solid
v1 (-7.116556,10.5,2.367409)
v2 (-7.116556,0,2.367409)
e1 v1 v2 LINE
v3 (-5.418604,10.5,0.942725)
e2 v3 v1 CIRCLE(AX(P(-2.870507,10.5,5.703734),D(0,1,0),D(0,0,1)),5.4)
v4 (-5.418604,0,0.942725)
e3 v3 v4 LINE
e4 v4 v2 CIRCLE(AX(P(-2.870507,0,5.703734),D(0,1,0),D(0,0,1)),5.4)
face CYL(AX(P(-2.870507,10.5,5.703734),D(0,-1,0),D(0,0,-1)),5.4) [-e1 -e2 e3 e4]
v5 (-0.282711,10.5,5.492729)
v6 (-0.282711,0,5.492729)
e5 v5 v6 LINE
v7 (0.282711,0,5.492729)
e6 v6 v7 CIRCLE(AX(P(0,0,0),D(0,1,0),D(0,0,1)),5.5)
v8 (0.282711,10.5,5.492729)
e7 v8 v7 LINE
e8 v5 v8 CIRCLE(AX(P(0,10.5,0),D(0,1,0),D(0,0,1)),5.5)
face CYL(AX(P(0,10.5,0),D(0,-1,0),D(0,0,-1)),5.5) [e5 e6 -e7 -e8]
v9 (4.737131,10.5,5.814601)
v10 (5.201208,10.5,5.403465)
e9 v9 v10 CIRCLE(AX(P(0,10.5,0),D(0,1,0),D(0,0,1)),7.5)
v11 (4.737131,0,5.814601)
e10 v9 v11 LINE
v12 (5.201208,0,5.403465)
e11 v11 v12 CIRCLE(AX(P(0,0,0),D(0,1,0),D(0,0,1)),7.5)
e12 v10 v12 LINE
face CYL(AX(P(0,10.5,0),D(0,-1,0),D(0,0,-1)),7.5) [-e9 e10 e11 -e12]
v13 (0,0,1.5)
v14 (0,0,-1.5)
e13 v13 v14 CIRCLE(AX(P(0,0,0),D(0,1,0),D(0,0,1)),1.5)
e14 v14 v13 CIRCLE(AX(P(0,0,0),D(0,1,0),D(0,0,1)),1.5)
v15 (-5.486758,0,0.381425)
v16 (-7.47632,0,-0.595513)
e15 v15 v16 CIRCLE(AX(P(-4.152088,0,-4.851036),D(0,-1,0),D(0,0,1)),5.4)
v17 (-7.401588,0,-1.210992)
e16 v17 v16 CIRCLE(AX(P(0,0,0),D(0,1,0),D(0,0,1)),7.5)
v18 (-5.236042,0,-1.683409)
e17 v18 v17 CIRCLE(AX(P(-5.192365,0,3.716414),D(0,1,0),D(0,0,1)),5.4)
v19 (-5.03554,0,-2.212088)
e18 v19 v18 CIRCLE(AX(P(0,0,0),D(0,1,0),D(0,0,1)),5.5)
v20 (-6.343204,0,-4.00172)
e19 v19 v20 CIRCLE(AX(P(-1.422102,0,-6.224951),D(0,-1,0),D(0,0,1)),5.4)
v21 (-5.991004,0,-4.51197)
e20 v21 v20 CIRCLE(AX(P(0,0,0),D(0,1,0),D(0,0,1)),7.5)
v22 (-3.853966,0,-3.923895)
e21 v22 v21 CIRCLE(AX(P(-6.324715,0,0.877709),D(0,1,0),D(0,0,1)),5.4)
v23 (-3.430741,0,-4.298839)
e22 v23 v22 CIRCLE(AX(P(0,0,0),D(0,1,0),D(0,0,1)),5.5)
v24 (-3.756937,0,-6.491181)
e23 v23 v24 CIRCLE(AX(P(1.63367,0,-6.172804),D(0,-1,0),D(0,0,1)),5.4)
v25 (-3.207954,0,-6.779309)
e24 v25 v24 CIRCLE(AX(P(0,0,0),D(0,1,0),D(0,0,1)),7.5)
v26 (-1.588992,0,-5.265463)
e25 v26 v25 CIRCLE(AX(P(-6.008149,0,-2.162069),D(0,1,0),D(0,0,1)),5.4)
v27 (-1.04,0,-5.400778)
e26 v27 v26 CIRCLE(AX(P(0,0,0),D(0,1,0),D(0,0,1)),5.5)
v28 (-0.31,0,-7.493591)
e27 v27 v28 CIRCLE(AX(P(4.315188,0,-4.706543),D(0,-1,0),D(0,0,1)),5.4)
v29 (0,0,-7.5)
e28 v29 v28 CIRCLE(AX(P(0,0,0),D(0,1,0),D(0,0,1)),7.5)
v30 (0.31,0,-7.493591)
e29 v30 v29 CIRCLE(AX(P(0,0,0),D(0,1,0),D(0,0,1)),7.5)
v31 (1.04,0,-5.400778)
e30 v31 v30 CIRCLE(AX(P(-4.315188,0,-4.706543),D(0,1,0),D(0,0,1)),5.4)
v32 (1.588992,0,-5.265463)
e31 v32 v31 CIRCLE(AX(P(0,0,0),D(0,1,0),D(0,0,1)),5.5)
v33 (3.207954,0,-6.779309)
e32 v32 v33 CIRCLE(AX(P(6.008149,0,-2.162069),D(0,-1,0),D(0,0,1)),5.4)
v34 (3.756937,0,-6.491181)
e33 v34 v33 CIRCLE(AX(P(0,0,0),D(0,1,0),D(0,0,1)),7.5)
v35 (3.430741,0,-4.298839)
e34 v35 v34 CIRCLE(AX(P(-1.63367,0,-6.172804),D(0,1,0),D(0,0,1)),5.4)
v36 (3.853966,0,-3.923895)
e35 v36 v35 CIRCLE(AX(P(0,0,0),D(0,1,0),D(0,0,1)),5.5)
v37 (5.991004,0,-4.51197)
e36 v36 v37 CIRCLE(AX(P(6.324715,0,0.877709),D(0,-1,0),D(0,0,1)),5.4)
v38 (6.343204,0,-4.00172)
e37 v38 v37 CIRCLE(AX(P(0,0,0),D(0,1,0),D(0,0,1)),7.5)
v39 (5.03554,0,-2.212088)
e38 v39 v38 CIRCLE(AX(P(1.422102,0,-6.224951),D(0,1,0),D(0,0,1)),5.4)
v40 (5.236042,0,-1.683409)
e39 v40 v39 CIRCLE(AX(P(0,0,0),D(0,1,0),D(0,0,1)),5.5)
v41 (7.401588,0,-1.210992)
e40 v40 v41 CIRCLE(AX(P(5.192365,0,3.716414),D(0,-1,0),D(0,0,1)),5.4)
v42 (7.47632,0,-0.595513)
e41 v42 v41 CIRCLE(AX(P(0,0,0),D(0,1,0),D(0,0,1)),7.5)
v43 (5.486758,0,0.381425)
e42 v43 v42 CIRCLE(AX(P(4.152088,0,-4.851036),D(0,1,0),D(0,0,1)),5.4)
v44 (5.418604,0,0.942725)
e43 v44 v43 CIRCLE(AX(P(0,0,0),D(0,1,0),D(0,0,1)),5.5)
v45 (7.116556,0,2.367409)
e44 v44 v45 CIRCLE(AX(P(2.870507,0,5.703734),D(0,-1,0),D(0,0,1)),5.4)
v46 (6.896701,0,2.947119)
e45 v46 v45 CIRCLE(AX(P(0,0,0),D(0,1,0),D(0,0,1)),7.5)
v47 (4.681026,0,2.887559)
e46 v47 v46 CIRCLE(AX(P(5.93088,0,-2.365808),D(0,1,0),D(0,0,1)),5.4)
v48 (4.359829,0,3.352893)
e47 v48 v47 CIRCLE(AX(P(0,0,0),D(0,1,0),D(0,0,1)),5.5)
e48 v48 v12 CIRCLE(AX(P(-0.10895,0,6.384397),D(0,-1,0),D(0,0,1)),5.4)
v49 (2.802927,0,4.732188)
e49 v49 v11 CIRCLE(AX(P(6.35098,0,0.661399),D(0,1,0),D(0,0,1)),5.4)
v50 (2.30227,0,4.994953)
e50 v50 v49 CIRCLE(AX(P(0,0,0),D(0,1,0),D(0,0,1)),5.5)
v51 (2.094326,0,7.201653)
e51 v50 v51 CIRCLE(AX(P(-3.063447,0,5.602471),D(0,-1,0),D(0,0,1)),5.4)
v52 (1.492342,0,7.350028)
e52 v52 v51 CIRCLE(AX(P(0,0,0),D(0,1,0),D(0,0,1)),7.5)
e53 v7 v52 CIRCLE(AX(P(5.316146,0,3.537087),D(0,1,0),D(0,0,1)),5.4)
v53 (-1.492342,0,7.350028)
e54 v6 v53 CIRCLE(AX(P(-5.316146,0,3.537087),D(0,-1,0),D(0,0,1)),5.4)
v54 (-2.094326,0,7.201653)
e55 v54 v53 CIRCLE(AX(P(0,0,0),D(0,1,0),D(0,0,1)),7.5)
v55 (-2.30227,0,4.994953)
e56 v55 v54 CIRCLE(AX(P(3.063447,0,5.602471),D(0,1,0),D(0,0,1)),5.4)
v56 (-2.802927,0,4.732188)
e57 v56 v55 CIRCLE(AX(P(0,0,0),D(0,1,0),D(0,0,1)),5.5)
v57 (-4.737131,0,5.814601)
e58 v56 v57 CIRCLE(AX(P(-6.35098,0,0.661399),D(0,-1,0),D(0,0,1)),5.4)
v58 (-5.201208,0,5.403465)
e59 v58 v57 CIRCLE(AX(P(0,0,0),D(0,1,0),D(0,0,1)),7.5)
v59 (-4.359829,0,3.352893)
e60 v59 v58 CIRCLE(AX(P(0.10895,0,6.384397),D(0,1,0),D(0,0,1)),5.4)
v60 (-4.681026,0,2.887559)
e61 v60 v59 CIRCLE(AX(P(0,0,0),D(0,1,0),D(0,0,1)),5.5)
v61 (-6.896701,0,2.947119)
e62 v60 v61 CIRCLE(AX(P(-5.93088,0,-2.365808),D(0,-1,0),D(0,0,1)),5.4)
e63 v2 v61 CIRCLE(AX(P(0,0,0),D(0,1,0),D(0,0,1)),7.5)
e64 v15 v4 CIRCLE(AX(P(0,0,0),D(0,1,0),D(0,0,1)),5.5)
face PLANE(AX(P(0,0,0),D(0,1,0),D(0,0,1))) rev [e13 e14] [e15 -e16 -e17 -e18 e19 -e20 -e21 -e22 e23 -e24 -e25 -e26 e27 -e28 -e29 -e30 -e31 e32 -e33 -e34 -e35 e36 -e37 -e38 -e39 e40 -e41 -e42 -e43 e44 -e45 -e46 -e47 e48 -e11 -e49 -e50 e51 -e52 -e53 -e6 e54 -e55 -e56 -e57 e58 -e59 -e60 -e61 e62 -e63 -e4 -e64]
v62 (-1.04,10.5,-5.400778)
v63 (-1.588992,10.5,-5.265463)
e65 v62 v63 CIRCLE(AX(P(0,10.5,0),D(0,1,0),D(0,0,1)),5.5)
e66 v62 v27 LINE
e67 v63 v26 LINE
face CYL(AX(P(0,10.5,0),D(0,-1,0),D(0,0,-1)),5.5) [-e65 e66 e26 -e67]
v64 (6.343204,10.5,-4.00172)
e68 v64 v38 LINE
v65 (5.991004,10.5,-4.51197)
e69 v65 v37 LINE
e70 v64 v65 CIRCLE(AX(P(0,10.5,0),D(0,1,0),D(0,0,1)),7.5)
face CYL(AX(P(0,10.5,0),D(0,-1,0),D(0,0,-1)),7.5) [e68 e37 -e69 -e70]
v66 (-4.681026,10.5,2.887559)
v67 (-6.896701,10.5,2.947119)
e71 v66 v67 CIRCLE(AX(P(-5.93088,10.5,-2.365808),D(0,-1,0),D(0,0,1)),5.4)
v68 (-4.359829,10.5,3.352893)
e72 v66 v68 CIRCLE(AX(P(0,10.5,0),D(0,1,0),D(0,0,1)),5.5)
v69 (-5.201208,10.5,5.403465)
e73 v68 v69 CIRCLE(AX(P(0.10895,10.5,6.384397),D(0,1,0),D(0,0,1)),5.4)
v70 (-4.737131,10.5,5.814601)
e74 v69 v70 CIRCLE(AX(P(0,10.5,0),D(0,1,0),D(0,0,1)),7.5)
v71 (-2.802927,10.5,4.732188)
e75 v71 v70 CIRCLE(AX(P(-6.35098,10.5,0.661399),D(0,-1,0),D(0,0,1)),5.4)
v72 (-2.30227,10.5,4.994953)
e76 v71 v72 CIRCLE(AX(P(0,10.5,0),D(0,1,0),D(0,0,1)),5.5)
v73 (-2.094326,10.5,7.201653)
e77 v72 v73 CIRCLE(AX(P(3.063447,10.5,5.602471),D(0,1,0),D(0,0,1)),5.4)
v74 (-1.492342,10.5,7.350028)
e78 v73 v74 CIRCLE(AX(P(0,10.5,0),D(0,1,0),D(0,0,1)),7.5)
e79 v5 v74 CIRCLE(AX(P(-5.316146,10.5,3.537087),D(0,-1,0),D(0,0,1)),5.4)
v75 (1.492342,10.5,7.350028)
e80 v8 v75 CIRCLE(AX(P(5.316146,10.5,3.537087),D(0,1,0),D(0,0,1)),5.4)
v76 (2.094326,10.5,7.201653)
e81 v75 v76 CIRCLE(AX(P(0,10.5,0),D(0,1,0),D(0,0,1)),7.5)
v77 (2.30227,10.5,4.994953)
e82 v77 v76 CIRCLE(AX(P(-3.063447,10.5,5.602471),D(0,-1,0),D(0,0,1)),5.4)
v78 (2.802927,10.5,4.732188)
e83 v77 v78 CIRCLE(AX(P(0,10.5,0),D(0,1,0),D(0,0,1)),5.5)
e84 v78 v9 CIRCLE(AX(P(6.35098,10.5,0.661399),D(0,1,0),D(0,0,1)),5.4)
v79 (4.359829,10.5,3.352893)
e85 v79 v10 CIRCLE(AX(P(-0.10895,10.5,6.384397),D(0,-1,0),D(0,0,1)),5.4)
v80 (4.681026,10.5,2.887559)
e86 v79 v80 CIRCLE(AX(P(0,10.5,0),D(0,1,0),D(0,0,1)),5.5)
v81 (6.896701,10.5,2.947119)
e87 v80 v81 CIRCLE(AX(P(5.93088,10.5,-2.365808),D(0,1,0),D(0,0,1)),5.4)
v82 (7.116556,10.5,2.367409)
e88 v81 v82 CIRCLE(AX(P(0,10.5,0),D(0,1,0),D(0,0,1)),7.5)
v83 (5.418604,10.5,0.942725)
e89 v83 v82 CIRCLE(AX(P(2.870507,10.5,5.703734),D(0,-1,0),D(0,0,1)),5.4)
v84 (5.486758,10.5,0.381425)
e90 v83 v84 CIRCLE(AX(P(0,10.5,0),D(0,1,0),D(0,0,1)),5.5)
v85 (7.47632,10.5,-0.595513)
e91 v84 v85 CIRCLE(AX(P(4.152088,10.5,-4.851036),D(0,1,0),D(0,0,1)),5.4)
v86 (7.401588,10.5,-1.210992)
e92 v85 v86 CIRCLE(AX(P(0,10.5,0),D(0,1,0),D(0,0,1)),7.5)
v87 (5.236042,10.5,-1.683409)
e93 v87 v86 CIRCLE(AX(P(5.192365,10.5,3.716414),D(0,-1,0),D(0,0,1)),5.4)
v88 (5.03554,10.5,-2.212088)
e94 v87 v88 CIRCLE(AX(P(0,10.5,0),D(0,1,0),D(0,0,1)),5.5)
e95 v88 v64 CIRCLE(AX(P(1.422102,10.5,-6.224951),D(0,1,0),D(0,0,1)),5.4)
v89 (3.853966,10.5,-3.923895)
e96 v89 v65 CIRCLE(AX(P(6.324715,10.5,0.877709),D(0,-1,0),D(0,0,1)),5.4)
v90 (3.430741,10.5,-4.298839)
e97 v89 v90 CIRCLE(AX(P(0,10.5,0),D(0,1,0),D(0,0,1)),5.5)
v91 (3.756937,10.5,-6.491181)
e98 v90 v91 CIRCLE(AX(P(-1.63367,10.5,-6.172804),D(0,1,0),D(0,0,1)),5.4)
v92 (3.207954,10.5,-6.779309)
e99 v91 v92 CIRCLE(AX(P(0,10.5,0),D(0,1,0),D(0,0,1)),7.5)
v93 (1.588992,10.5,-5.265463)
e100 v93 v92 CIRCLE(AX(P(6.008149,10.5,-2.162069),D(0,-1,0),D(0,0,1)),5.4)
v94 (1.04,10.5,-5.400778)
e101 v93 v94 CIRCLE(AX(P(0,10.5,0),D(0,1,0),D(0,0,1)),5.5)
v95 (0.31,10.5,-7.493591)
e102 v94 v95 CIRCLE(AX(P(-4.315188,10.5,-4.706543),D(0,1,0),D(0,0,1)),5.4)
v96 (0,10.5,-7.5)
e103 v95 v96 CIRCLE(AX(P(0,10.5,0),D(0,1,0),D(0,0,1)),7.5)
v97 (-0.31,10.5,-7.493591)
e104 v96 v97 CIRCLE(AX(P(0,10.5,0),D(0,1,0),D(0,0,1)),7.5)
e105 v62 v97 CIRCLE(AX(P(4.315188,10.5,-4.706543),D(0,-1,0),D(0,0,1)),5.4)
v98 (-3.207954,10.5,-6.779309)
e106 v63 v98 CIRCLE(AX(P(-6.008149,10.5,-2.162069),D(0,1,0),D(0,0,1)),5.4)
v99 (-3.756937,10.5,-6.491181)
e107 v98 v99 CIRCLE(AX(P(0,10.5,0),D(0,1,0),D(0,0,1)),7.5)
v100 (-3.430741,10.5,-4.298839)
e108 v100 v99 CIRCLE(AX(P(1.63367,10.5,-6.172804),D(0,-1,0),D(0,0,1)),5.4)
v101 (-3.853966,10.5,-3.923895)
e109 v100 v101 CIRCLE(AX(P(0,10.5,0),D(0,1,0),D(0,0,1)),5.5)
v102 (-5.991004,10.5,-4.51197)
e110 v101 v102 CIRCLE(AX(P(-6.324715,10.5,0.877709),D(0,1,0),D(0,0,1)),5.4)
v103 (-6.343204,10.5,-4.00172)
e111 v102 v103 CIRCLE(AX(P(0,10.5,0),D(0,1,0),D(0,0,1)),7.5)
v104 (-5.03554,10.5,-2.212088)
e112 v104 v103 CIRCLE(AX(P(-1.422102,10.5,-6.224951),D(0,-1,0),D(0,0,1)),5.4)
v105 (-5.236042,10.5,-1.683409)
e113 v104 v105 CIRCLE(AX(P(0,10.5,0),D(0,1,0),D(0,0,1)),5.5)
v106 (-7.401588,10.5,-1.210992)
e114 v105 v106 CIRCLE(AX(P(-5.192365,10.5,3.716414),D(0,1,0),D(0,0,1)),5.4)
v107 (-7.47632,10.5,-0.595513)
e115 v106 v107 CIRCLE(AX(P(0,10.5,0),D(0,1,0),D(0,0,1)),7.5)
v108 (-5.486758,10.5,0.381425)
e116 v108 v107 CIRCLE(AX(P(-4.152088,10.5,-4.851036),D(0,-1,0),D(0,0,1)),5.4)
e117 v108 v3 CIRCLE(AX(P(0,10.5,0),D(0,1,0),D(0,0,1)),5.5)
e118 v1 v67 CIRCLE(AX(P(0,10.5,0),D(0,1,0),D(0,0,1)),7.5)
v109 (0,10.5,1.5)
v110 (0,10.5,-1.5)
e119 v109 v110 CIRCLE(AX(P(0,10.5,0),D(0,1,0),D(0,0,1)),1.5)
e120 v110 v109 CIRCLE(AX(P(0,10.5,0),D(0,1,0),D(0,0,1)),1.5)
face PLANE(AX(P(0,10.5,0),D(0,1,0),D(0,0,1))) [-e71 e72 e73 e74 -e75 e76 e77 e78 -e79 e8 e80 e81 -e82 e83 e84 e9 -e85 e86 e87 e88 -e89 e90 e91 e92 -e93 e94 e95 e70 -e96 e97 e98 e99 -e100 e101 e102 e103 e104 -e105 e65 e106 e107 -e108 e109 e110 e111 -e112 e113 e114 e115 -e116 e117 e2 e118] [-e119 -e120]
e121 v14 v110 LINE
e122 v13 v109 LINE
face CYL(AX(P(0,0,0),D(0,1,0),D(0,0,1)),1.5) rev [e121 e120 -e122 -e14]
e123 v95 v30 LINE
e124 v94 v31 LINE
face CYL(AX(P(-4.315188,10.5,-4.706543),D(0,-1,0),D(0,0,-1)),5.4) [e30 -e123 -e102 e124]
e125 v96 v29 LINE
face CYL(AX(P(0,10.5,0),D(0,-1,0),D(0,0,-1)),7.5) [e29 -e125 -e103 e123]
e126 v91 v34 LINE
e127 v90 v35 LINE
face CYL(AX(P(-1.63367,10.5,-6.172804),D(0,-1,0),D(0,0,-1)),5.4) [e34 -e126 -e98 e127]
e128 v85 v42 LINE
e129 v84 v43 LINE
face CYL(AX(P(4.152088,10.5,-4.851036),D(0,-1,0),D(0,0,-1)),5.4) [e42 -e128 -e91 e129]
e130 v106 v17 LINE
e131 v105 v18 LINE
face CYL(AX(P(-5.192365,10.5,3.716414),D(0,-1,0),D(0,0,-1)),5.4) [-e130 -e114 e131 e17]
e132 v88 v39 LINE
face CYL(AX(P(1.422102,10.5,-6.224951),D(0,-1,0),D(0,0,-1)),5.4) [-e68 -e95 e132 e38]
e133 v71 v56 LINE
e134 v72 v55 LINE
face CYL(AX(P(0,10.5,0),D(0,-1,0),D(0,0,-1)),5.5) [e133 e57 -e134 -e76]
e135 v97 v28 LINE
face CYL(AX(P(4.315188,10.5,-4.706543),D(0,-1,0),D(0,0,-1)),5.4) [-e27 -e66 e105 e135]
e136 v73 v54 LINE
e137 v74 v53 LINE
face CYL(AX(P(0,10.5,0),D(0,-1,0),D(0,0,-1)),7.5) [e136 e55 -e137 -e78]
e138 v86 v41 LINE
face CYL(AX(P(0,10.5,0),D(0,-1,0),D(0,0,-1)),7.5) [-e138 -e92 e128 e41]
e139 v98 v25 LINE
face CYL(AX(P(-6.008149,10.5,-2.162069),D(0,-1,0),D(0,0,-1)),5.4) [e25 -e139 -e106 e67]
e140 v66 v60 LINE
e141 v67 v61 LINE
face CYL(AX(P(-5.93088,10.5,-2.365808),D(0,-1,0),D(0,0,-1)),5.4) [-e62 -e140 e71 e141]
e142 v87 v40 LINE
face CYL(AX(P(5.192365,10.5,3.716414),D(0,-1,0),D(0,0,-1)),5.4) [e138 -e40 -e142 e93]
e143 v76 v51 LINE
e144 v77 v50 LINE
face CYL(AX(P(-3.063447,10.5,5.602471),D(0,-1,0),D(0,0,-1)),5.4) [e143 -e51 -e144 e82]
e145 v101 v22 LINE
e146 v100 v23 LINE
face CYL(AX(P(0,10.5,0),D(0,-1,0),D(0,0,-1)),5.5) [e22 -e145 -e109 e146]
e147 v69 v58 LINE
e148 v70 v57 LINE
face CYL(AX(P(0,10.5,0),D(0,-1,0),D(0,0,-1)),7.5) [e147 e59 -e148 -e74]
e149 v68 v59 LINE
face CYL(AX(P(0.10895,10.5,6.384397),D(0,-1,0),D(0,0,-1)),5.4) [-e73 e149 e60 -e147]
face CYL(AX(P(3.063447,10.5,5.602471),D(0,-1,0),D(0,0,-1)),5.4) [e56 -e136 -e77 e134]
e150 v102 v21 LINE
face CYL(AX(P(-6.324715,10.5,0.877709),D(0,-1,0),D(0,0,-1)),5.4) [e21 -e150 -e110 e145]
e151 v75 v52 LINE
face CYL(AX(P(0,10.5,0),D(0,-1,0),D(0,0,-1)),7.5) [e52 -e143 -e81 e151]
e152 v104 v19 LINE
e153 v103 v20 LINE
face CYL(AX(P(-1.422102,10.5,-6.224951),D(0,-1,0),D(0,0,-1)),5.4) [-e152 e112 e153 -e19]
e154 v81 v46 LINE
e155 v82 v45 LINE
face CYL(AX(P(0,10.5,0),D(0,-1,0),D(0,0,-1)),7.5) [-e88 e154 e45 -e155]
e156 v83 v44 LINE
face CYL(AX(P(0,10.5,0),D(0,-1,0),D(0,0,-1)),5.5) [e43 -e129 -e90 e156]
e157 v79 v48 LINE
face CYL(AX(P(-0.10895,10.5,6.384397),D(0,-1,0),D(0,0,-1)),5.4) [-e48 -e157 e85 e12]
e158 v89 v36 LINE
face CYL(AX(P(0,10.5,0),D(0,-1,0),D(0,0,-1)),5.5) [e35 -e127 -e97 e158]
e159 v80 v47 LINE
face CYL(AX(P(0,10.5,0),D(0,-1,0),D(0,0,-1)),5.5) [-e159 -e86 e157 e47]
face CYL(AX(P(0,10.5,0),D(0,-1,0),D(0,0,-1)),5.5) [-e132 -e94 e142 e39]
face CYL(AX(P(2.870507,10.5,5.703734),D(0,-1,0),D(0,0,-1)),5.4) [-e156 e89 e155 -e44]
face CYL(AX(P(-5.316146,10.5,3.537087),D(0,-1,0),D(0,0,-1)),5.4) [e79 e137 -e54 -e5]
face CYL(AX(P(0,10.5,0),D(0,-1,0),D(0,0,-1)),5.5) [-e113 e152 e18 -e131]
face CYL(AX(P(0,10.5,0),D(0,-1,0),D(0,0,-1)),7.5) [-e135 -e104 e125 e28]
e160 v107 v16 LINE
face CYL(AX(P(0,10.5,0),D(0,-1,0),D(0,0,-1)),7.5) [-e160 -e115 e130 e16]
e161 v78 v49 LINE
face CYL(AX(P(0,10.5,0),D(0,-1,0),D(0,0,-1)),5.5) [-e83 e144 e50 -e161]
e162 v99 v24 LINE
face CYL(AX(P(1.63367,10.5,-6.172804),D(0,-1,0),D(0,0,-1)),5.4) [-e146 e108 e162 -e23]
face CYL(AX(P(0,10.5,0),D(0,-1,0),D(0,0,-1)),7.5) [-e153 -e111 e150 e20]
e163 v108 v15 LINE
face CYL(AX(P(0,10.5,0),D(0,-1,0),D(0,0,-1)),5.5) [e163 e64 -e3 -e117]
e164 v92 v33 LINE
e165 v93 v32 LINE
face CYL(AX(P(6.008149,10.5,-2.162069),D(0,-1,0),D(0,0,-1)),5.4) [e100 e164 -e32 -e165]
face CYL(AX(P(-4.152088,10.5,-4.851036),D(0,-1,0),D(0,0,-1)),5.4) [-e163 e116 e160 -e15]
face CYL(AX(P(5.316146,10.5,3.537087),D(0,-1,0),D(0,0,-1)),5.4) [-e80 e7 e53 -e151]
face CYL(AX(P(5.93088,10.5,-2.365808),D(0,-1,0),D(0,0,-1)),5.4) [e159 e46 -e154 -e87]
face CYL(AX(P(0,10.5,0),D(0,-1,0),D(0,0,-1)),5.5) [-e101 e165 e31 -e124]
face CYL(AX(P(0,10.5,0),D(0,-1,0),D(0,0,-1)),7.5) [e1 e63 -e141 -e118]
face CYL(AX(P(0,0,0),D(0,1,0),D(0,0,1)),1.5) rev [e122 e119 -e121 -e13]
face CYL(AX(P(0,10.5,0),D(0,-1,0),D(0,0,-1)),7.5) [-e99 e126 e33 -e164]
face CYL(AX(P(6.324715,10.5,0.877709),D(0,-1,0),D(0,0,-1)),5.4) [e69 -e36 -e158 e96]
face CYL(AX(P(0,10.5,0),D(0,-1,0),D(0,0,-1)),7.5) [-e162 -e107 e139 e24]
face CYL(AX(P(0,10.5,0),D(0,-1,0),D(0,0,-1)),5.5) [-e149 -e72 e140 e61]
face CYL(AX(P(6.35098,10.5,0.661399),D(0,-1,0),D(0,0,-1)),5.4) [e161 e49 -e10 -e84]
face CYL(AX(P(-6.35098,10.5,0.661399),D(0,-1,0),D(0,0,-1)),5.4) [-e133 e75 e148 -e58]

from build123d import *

# Parameters (mm, degrees)
BOSS_EXTRUDE1_DEPTH = 10.5
SKETCH2_R           = 1.5
CUT_EXTRUDE1_DEPTH  = 10.5


with BuildPart() as part:
    # Sketch1 → Boss-Extrude1 (new body)
    with BuildSketch(Plane(origin=(0, 0, 0), x_dir=(1, 0, 0), z_dir=(0, 1, 0))):
        with BuildLine():
            ThreePointArc((1.04, 5.400777722), (0.783531714, 6.485041414), (0.31, 7.493590595))
            ThreePointArc((0.31, 7.493590595), (0, 7.5), (-0.31, 7.493590595))
            ThreePointArc((-0.31, 7.493590595), (-0.783531714, 6.485041414), (-1.04, 5.400777722))
            ThreePointArc((-1.04, 5.400777722), (-1.316236154, 5.340179996), (-1.588992288, 5.265463276))
            ThreePointArc((-1.588992288, 5.265463276), (-2.319966139, 6.10634434), (-3.207953823, 6.779309129))
            ThreePointArc((-3.207953823, 6.779309129), (-3.48542379, 6.640920192), (-3.756936559, 6.491180762))
            ThreePointArc((-3.756936559, 6.491180762), (-3.707531894, 5.378093653), (-3.430740821, 4.298839078))
            ThreePointArc((-3.430740821, 4.298839078), (-3.64717462, 4.116809115), (-3.853965592, 3.923894649))
            ThreePointArc((-3.853965592, 3.923894649), (-4.891987708, 4.328757368), (-5.991004086, 4.511969642))
            ThreePointArc((-5.991004086, 4.511969642), (-6.172378994, 4.2604856), (-6.343204228, 4.001719645))
            ThreePointArc((-6.343204228, 4.001719645), (-5.782181198, 3.039089449), (-5.035540265, 2.212088208))
            ThreePointArc((-5.035540265, 2.212088208), (-5.142589335, 1.950326879), (-5.236041824, 1.683409046))
            ThreePointArc((-5.236041824, 1.683409046), (-6.343313848, 1.559504249), (-7.401587511, 1.210992284))
            ThreePointArc((-7.401587511, 1.210992284), (-7.445316556, 0.904025102), (-7.476320253, 0.595512782))
            ThreePointArc((-7.476320253, 0.595512782), (-6.532202472, 0.003866477), (-5.486758119, -0.381425412))
            ThreePointArc((-5.486758119, -0.381425412), (-5.459898808, -0.662951741), (-5.418603976, -0.942725282))
            ThreePointArc((-5.418603976, -0.942725282), (-6.341463231, -1.567012498), (-7.116556437, -2.367408811))
            ThreePointArc((-7.116556437, -2.367408811), (-7.01262182, -2.659536653), (-6.896701407, -2.947118882))
            ThreePointArc((-6.896701407, -2.947118882), (-5.785774881, -3.032242258), (-4.68102581, -2.887559066))
            ThreePointArc((-4.68102581, -2.887559066), (-4.526411262, -3.124356107), (-4.359829258, -3.352892609))
            ThreePointArc((-4.359829258, -3.352892609), (-4.886859811, -4.334545567), (-5.201208047, -5.403465078))
            ThreePointArc((-5.201208047, -5.403465078), (-4.973419937, -5.613830611), (-4.737131383, -5.814601127))
            ThreePointArc((-4.737131383, -5.814601127), (-3.713895991, -5.373700834), (-2.802926901, -4.732187738))
            ThreePointArc((-2.802926901, -4.732187738), (-2.555977446, -4.870008141), (-2.302270198, -4.994952646))
            ThreePointArc((-2.302270198, -4.994952646), (-2.312735701, -6.109086484), (-2.094325574, -7.201652615))
            ThreePointArc((-2.094325574, -7.201652615), (-1.794867482, -7.282063631), (-1.492341648, -7.350028327))
            ThreePointArc((-1.492341648, -7.350028327), (-0.791208287, -6.484109309), (-0.282711218, -5.492729228))
            ThreePointArc((-0.282711218, -5.492729228), (0, -5.5), (0.282711218, -5.492729228))
            ThreePointArc((0.282711218, -5.492729228), (0.791208287, -6.484109309), (1.492341648, -7.350028327))
            ThreePointArc((1.492341648, -7.350028327), (1.794867482, -7.282063631), (2.094325574, -7.201652615))
            ThreePointArc((2.094325574, -7.201652615), (2.312735701, -6.109086484), (2.302270198, -4.994952646))
            ThreePointArc((2.302270198, -4.994952646), (2.555977446, -4.870008141), (2.802926901, -4.732187738))
            ThreePointArc((2.802926901, -4.732187738), (3.713895991, -5.373700834), (4.737131383, -5.814601127))
            ThreePointArc((4.737131383, -5.814601127), (4.973419937, -5.613830611), (5.201208047, -5.403465078))
            ThreePointArc((5.201208047, -5.403465078), (4.886859811, -4.334545567), (4.359829258, -3.352892609))
            ThreePointArc((4.359829258, -3.352892609), (4.526411262, -3.124356107), (4.68102581, -2.887559066))
            ThreePointArc((4.68102581, -2.887559066), (5.785774881, -3.032242258), (6.896701407, -2.947118882))
            ThreePointArc((6.896701407, -2.947118882), (7.01262182, -2.659536653), (7.116556437, -2.367408811))
            ThreePointArc((7.116556437, -2.367408811), (6.341463231, -1.567012498), (5.418603976, -0.942725282))
            ThreePointArc((5.418603976, -0.942725282), (5.459898808, -0.662951741), (5.486758119, -0.381425412))
            ThreePointArc((5.486758119, -0.381425412), (6.532202472, 0.003866477), (7.476320253, 0.595512782))
            ThreePointArc((7.476320253, 0.595512782), (7.445316556, 0.904025102), (7.401587511, 1.210992284))
            ThreePointArc((7.401587511, 1.210992284), (6.343313848, 1.559504249), (5.236041824, 1.683409046))
            ThreePointArc((5.236041824, 1.683409046), (5.142589335, 1.950326879), (5.035540265, 2.212088208))
            ThreePointArc((5.035540265, 2.212088208), (5.782181198, 3.039089449), (6.343204228, 4.001719645))
            ThreePointArc((6.343204228, 4.001719645), (6.172378994, 4.2604856), (5.991004086, 4.511969642))
            ThreePointArc((5.991004086, 4.511969642), (4.891987708, 4.328757368), (3.853965592, 3.923894649))
            ThreePointArc((3.853965592, 3.923894649), (3.64717462, 4.116809115), (3.430740821, 4.298839078))
            ThreePointArc((3.430740821, 4.298839078), (3.707531894, 5.378093653), (3.756936559, 6.491180762))
            ThreePointArc((3.756936559, 6.491180762), (3.48542379, 6.640920192), (3.207953823, 6.779309129))
            ThreePointArc((3.207953823, 6.779309129), (2.319966139, 6.10634434), (1.588992288, 5.265463276))
            ThreePointArc((1.588992288, 5.265463276), (1.316236154, 5.340179996), (1.04, 5.400777722))
        make_face()
    extrude(amount=BOSS_EXTRUDE1_DEPTH)

    # Sketch2 → Cut-Extrude1 (cut)
    with BuildSketch(Plane(origin=(0, 10.5, 0), x_dir=(1, 0, 0), z_dir=(0, 1, 0))):
        with Locations(Location((0, 0, 0), (0, 0, 270))):
            Circle(SKETCH2_R)
    extrude(amount=-CUT_EXTRUDE1_DEPTH, mode=Mode.SUBTRACT)


solid = part.part
